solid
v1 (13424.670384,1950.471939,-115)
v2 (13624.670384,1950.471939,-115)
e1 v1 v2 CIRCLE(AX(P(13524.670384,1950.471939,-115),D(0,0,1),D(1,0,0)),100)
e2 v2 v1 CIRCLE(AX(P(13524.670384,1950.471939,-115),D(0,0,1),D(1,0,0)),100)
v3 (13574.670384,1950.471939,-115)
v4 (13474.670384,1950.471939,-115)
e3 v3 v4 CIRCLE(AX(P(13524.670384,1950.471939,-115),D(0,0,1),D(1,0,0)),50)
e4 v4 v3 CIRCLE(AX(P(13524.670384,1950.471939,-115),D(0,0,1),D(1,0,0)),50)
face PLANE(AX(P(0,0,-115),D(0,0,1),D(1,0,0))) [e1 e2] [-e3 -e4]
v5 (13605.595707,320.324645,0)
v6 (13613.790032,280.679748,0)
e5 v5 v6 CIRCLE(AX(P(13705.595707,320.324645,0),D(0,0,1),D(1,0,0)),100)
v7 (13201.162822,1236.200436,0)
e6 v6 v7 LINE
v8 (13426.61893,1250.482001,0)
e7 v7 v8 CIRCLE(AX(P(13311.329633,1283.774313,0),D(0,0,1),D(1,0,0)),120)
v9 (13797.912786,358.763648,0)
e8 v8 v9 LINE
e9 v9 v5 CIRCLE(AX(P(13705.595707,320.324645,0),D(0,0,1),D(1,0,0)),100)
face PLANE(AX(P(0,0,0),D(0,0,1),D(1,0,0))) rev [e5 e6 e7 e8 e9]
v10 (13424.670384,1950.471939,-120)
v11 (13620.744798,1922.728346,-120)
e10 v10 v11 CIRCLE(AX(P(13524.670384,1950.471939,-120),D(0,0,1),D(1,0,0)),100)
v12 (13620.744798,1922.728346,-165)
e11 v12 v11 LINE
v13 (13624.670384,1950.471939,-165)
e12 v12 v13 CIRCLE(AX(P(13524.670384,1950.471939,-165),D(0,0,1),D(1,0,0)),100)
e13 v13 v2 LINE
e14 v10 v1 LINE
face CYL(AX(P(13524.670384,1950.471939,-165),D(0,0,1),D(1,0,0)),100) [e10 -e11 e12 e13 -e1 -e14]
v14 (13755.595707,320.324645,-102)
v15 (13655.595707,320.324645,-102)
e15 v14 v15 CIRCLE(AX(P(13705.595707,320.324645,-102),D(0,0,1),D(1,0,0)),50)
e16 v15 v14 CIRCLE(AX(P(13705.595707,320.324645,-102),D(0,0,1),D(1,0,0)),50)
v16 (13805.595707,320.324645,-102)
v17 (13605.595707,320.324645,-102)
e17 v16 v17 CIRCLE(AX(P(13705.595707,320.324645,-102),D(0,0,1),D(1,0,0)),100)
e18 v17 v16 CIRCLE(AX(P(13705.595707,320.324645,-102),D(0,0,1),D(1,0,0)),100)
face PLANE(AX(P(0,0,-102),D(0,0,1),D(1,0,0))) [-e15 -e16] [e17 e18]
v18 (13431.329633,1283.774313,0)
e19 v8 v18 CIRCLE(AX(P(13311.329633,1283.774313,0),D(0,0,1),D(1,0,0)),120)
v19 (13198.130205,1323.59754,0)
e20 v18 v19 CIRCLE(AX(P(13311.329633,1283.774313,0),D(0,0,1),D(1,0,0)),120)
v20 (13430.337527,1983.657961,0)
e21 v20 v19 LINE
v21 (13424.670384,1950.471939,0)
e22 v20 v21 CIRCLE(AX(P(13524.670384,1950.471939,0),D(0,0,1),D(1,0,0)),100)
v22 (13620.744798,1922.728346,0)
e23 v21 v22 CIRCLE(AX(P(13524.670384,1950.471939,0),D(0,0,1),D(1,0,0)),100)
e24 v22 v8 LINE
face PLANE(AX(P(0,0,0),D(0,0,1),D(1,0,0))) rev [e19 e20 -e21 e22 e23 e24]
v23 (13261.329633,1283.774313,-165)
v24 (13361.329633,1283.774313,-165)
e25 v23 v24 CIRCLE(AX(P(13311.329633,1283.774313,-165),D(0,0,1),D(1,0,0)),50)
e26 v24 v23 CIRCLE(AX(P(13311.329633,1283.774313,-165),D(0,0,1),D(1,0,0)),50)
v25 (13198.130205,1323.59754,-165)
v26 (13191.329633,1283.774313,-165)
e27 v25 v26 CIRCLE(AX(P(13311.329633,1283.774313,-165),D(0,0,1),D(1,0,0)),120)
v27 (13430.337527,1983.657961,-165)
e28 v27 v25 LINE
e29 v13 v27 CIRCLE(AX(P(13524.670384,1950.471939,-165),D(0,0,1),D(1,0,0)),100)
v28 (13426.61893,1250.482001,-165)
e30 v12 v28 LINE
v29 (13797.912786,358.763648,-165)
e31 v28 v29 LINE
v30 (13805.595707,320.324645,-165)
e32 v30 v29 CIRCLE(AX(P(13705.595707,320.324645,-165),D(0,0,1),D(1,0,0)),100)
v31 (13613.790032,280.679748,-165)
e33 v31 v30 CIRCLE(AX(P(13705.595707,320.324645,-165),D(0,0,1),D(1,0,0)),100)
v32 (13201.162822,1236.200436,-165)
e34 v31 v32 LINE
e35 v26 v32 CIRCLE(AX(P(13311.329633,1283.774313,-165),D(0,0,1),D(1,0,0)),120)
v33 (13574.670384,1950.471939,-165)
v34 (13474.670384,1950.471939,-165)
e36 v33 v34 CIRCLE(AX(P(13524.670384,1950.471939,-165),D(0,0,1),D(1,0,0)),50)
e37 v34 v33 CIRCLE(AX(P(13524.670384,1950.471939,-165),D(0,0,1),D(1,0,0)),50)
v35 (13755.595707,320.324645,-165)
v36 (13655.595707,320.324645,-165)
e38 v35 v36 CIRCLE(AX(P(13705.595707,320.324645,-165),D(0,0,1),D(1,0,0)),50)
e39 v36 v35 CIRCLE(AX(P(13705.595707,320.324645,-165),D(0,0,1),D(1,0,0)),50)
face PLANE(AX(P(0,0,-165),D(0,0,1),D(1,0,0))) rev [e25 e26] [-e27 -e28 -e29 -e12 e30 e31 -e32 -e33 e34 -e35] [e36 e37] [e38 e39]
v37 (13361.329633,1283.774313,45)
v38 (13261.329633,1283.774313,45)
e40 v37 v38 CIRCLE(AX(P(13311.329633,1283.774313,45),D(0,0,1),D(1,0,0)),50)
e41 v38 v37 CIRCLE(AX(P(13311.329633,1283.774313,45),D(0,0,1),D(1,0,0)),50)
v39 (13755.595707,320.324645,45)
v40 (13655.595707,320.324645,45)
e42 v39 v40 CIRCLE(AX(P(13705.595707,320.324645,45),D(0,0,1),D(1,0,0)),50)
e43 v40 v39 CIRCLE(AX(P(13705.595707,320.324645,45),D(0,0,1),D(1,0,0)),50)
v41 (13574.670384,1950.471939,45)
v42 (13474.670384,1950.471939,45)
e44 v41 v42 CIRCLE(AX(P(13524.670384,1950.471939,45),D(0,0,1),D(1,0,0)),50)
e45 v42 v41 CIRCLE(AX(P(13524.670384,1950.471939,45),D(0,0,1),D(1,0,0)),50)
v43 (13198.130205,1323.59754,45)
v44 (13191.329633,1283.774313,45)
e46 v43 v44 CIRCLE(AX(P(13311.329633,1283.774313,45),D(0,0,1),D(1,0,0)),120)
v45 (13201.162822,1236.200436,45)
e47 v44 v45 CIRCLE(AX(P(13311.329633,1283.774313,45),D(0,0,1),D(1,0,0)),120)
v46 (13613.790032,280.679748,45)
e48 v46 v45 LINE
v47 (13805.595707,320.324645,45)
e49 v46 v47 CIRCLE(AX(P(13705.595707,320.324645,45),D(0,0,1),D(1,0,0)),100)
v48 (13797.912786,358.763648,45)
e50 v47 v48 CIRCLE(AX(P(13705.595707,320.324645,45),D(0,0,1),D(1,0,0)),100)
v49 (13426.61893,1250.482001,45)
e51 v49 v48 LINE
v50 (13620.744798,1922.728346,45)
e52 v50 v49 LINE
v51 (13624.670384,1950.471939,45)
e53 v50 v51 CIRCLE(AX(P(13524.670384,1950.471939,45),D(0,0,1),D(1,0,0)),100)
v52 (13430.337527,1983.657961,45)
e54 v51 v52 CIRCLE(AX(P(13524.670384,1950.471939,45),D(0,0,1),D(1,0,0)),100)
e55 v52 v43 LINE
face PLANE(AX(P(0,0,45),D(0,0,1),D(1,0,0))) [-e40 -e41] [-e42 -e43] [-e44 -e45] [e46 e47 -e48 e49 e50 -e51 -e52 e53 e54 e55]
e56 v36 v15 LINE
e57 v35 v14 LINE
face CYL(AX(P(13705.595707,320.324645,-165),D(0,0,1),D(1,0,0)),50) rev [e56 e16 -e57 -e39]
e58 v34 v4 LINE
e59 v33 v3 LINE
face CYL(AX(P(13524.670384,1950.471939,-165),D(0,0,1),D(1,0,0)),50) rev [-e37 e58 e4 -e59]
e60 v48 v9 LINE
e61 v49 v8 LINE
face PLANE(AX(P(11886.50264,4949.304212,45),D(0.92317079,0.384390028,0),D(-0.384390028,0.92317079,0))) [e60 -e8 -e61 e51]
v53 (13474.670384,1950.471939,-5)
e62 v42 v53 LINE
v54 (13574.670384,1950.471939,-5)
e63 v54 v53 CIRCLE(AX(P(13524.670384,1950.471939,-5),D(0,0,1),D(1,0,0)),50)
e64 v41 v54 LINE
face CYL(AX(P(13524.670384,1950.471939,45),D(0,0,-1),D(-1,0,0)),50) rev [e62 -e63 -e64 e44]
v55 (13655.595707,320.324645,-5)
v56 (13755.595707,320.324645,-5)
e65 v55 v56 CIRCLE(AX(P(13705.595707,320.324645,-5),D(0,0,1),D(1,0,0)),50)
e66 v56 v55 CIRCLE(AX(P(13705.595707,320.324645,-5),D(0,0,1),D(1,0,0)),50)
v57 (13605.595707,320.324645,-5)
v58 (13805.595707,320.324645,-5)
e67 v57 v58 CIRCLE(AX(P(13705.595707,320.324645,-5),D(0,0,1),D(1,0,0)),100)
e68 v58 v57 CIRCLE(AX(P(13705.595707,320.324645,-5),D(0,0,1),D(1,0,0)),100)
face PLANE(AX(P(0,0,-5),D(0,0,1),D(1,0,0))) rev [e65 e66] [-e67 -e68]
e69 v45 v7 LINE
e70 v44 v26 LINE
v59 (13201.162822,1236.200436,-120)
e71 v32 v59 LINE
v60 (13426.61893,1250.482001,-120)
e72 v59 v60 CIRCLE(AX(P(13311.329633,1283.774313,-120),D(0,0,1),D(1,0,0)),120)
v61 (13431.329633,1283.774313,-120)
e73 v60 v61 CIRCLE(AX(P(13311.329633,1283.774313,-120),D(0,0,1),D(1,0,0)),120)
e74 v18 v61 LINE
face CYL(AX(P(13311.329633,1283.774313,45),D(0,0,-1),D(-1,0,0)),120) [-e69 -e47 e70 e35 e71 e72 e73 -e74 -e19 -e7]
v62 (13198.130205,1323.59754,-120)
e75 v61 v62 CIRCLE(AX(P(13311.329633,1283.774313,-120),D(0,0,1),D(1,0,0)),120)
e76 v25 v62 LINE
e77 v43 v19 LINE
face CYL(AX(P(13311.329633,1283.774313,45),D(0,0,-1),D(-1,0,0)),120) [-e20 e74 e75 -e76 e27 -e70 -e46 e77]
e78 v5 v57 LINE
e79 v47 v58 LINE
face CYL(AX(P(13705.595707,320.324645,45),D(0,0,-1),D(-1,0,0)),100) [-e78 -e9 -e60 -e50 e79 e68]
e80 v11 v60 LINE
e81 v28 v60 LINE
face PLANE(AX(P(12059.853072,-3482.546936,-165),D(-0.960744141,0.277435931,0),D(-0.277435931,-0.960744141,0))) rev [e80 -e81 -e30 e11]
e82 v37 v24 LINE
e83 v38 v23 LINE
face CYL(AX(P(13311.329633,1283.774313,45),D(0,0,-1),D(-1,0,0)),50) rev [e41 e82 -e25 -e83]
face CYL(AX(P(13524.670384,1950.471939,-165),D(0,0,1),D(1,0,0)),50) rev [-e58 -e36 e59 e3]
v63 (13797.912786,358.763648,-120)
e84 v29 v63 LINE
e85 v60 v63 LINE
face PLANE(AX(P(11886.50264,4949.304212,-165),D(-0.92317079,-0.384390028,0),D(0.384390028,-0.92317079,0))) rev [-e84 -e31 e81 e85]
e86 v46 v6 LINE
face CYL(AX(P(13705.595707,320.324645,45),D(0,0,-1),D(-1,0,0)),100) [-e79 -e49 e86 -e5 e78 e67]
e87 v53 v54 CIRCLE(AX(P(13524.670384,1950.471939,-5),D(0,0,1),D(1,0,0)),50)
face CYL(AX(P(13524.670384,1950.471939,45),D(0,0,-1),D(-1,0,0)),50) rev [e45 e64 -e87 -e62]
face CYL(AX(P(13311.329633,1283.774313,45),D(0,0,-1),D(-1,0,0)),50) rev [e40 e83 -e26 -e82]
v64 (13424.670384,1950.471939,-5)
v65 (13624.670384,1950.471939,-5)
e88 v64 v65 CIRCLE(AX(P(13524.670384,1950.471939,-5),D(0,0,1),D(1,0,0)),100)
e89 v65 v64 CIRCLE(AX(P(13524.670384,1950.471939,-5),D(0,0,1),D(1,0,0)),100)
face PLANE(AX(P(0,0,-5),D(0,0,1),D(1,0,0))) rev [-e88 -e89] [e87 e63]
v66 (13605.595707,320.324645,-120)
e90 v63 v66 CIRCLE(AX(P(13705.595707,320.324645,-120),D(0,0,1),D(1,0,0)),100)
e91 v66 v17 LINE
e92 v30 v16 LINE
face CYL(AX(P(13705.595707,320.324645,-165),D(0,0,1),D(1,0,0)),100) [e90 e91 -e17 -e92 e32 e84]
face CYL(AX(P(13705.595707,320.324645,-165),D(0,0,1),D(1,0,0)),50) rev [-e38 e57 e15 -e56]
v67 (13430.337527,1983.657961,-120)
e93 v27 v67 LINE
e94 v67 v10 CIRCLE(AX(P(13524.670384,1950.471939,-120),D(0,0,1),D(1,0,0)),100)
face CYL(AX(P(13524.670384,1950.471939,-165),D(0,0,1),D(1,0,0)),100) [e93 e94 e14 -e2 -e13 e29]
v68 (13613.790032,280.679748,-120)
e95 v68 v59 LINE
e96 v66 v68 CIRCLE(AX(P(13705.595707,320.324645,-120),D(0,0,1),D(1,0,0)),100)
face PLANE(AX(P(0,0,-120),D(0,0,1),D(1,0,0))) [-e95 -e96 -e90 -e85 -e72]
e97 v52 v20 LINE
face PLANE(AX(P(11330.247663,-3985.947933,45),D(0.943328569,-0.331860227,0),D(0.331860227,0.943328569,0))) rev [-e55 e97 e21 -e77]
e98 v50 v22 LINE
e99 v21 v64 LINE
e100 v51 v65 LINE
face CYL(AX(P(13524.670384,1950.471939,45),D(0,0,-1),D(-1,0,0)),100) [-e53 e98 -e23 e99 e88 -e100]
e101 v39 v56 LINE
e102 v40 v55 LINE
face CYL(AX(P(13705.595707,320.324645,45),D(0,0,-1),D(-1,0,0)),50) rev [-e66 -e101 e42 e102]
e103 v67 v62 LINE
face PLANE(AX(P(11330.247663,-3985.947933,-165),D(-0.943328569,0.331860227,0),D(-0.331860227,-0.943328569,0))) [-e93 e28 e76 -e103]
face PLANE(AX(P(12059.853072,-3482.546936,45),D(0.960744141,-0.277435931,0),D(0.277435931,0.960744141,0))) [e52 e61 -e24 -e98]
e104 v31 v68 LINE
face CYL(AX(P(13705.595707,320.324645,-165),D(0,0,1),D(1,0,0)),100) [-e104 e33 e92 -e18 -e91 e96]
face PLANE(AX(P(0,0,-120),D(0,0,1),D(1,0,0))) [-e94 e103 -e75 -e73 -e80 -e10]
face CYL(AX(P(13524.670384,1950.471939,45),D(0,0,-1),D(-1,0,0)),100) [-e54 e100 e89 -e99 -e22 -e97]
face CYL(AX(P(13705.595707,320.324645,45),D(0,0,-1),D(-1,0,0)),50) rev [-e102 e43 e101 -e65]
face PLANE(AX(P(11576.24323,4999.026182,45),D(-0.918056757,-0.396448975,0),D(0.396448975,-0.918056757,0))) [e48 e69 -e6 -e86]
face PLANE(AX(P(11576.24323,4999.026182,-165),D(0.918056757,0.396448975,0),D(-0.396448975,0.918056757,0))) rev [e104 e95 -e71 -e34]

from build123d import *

# Parameters (mm, degrees)
SKETCH_1_8_R        = 100
SKETCH_1_8_R_2      = 50
SKETCH_1_8_R_3      = 120
BOSS_EXTRUDE1_DEPTH = 45
BOSS_EXTRUDE2_START = -120
SKETCH_1_3_R        = 120
SKETCH_1_3_R_2      = 50
BOSS_EXTRUDE2_DEPTH = 120
BOSS_EXTRUDE3_START = -5
SKETCH_1_4_R        = 100
SKETCH_1_4_R_2      = 50
BOSS_EXTRUDE3_DEPTH = 5
BOSS_EXTRUDE4_START = -120
SKETCH_1_6_R        = 120
SKETCH_1_6_R_2      = 50
SKETCH_1_6_R_3      = 100
BOSS_EXTRUDE4_DEPTH = 45
BOSS_EXTRUDE5_START = -120
SKETCH_1_7_R        = 50
BOSS_EXTRUDE5_DEPTH = 5
BOSS_EXTRUDE6_START = -120
SKETCH_1_8_2_R      = 50
BOSS_EXTRUDE6_DEPTH = 18


with BuildPart() as part:
    # Sketch 1_8 → Boss-Extrude1 (new body)
    # profile 1 of 5: a face of its own
    with BuildSketch(Plane.XY):
        with BuildLine():
            ThreePointArc((13620.744797989, 1922.728345575), (13494.193133773, 1855.229420726), (13430.337526965, 1983.657961365))
            Line((13430.337526965, 1983.657961365), (13198.130204679, 1323.597540284))
            ThreePointArc((13198.130204679, 1323.597540284), (13331.529491927, 1402.061952726), (13431.329633003, 1283.774313052))
            ThreePointArc((13431.329633003, 1283.774313052), (13430.146120976, 1266.962347499), (13426.618929907, 1250.482001337))
            Line((13426.618929907, 1250.482001337), (13620.744797989, 1922.728345575))
        make_face()
    # profile 2 of 5: a face of its own
    with BuildSketch(Plane.XY):
        with Locations((13524.670383902, 1950.471938671)):
            Circle(SKETCH_1_8_R)
        with Locations(Location((13524.670383902, 1950.471938671, 0), (0, 0, 180))):
            Circle(SKETCH_1_8_R_2, mode=Mode.SUBTRACT)
    # profile 3 of 5: a face of its own
    with BuildSketch(Plane.XY):
        with Locations((13311.329633003, 1283.774313052)):
            Circle(SKETCH_1_8_R_3)
        with Locations(Location((13311.329633003, 1283.774313052, 0), (0, 0, 180))):
            Circle(SKETCH_1_8_R_2, mode=Mode.SUBTRACT)
    # profile 4 of 5: a face of its own
    with BuildSketch(Plane.XY):
        with Locations((13705.595707248, 320.324645089)):
            Circle(SKETCH_1_8_R)
        with Locations(Location((13705.595707248, 320.324645089, 0), (0, 0, 180))):
            Circle(SKETCH_1_8_R_2, mode=Mode.SUBTRACT)
    # profile 5 of 5: a face of its own
    with BuildSketch(Plane.XY):
        with BuildLine():
            ThreePointArc((13426.618929907, 1250.482001337), (13318.91585359, 1164.014347884), (13201.162822108, 1236.200436006))
            Line((13201.162822108, 1236.200436006), (13613.790031502, 280.679747551))
            ThreePointArc((13613.790031502, 280.679747551), (13666.552919763, 412.387996893), (13797.912786205, 358.763647846))
            Line((13797.912786205, 358.763647846), (13426.618929907, 1250.482001337))
        make_face()
    extrude(amount=BOSS_EXTRUDE1_DEPTH)

    # 草图1<3> → Boss-Extrude2 (add)
    with BuildSketch(Plane.XY.offset(BOSS_EXTRUDE2_START)):
        with Locations(Location((13311.329633003, 1283.774313052, 0), (0, 0, 160.618277355))):
            Circle(SKETCH_1_3_R)
        with Locations(Location((13311.329633003, 1283.774313052, 0), (0, 0, 180))):
            Circle(SKETCH_1_3_R_2, mode=Mode.SUBTRACT)
    extrude(amount=BOSS_EXTRUDE2_DEPTH)

    # 草图1<4> → Boss-Extrude3 (add)
    # profile 1 of 2: a face of its own
    with BuildSketch(Plane.XY.offset(BOSS_EXTRUDE3_START)):
        with Locations(Location((13524.670383902, 1950.471938671, 0), (0, 0, 160.618277355))):
            Circle(SKETCH_1_4_R)
        with Locations(Location((13524.670383902, 1950.471938671, 0), (0, 0, 180))):
            Circle(SKETCH_1_4_R_2, mode=Mode.SUBTRACT)
    # profile 2 of 2: a face of its own
    with BuildSketch(Plane.XY.offset(BOSS_EXTRUDE3_START)):
        with Locations(Location((13705.595707248, 320.324645089, 0), (0, 0, 203.356373631))):
            Circle(SKETCH_1_4_R)
        with Locations(Location((13705.595707248, 320.324645089, 0), (0, 0, 180))):
            Circle(SKETCH_1_4_R_2, mode=Mode.SUBTRACT)
    extrude(amount=BOSS_EXTRUDE3_DEPTH)



with BuildPart() as body_2:
    # 草图1<6> → Boss-Extrude4 (new body)
    # profile 1 of 5: a face of its own
    with BuildSketch(Plane.XY.offset(BOSS_EXTRUDE4_START)):
        with BuildLine():
            ThreePointArc((13620.744797989, 1922.728345575), (13494.193133773, 1855.229420726), (13430.337526965, 1983.657961365))
            Line((13430.337526965, 1983.657961365), (13198.130204679, 1323.597540284))
            ThreePointArc((13198.130204679, 1323.597540284), (13331.529491927, 1402.061952726), (13431.329633003, 1283.774313052))
            ThreePointArc((13431.329633003, 1283.774313052), (13430.146120976, 1266.962347499), (13426.618929907, 1250.482001337))
            Line((13426.618929907, 1250.482001337), (13620.744797989, 1922.728345575))
        make_face()
    # profile 2 of 5: a face of its own
    with BuildSketch(Plane.XY.offset(BOSS_EXTRUDE4_START)):
        with BuildLine():
            ThreePointArc((13426.618929907, 1250.482001337), (13318.91585359, 1164.014347884), (13201.162822108, 1236.200436006))
            Line((13201.162822108, 1236.200436006), (13613.790031502, 280.679747551))
            ThreePointArc((13613.790031502, 280.679747551), (13666.552919763, 412.387996893), (13797.912786205, 358.763647846))
            Line((13797.912786205, 358.763647846), (13426.618929907, 1250.482001337))
        make_face()
    # profile 3 of 5: a face of its own
    with BuildSketch(Plane.XY.offset(BOSS_EXTRUDE4_START)):
        with Locations(Location((13311.329633003, 1283.774313052, 0), (0, 0, 160.618277355))):
            Circle(SKETCH_1_6_R)
        with Locations(Location((13311.329633003, 1283.774313052, 0), (0, 0, 180))):
            Circle(SKETCH_1_6_R_2, mode=Mode.SUBTRACT)
    # profile 4 of 5: a face of its own
    with BuildSketch(Plane.XY.offset(BOSS_EXTRUDE4_START)):
        with Locations(Location((13705.595707248, 320.324645089, 0), (0, 0, 203.356373631))):
            Circle(SKETCH_1_6_R_3)
        with Locations(Location((13705.595707248, 320.324645089, 0), (0, 0, 180))):
            Circle(SKETCH_1_6_R_2, mode=Mode.SUBTRACT)
    # profile 5 of 5: a face of its own
    with BuildSketch(Plane.XY.offset(BOSS_EXTRUDE4_START)):
        with Locations(Location((13524.670383902, 1950.471938671, 0), (0, 0, 160.618277355))):
            Circle(SKETCH_1_6_R_3)
        with Locations(Location((13524.670383902, 1950.471938671, 0), (0, 0, 180))):
            Circle(SKETCH_1_6_R_2, mode=Mode.SUBTRACT)
    extrude(amount=-BOSS_EXTRUDE4_DEPTH)


with BuildPart() as part_1:
    add(part.part)

    add(body_2.part)  # Boss-Extrude5 merges body 2
    # 草图1<7> → Boss-Extrude5 (add)
    with BuildSketch(Plane.XY.offset(BOSS_EXTRUDE5_START)):
        with BuildLine():
            ThreePointArc((13624.670383902, 1950.471938671), (13541.503599672, 2049.044971732), (13430.337526965, 1983.657961365))
            ThreePointArc((13430.337526965, 1983.657961365), (13494.193133773, 1855.229420726), (13620.744797989, 1922.728345575))
            ThreePointArc((13620.744797989, 1922.728345575), (13623.684123879, 1936.461967377), (13624.670383902, 1950.471938671))
        make_face()
        with Locations(Location((13524.670383902, 1950.471938671, 0), (0, 0, 180))):
            Circle(SKETCH_1_7_R, mode=Mode.SUBTRACT)
    extrude(amount=BOSS_EXTRUDE5_DEPTH)

    # Sketch 1_8 2 → Boss-Extrude6 (add)
    with BuildSketch(Plane.XY.offset(BOSS_EXTRUDE6_START)):
        with BuildLine():
            ThreePointArc((13797.912786205, 358.763647846), (13666.552919763, 412.387996893), (13613.790031502, 280.679747551))
            ThreePointArc((13613.790031502, 280.679747551), (13725.837155139, 222.39465077), (13805.595707248, 320.324645089))
            ThreePointArc((13805.595707248, 320.324645089), (13803.656167924, 339.924289274), (13797.912786205, 358.763647846))
        make_face()
        with Locations(Location((13705.595707248, 320.324645089, 0), (0, 0, 180))):
            Circle(SKETCH_1_8_2_R, mode=Mode.SUBTRACT)
    extrude(amount=BOSS_EXTRUDE6_DEPTH)


solid = part_1.part
